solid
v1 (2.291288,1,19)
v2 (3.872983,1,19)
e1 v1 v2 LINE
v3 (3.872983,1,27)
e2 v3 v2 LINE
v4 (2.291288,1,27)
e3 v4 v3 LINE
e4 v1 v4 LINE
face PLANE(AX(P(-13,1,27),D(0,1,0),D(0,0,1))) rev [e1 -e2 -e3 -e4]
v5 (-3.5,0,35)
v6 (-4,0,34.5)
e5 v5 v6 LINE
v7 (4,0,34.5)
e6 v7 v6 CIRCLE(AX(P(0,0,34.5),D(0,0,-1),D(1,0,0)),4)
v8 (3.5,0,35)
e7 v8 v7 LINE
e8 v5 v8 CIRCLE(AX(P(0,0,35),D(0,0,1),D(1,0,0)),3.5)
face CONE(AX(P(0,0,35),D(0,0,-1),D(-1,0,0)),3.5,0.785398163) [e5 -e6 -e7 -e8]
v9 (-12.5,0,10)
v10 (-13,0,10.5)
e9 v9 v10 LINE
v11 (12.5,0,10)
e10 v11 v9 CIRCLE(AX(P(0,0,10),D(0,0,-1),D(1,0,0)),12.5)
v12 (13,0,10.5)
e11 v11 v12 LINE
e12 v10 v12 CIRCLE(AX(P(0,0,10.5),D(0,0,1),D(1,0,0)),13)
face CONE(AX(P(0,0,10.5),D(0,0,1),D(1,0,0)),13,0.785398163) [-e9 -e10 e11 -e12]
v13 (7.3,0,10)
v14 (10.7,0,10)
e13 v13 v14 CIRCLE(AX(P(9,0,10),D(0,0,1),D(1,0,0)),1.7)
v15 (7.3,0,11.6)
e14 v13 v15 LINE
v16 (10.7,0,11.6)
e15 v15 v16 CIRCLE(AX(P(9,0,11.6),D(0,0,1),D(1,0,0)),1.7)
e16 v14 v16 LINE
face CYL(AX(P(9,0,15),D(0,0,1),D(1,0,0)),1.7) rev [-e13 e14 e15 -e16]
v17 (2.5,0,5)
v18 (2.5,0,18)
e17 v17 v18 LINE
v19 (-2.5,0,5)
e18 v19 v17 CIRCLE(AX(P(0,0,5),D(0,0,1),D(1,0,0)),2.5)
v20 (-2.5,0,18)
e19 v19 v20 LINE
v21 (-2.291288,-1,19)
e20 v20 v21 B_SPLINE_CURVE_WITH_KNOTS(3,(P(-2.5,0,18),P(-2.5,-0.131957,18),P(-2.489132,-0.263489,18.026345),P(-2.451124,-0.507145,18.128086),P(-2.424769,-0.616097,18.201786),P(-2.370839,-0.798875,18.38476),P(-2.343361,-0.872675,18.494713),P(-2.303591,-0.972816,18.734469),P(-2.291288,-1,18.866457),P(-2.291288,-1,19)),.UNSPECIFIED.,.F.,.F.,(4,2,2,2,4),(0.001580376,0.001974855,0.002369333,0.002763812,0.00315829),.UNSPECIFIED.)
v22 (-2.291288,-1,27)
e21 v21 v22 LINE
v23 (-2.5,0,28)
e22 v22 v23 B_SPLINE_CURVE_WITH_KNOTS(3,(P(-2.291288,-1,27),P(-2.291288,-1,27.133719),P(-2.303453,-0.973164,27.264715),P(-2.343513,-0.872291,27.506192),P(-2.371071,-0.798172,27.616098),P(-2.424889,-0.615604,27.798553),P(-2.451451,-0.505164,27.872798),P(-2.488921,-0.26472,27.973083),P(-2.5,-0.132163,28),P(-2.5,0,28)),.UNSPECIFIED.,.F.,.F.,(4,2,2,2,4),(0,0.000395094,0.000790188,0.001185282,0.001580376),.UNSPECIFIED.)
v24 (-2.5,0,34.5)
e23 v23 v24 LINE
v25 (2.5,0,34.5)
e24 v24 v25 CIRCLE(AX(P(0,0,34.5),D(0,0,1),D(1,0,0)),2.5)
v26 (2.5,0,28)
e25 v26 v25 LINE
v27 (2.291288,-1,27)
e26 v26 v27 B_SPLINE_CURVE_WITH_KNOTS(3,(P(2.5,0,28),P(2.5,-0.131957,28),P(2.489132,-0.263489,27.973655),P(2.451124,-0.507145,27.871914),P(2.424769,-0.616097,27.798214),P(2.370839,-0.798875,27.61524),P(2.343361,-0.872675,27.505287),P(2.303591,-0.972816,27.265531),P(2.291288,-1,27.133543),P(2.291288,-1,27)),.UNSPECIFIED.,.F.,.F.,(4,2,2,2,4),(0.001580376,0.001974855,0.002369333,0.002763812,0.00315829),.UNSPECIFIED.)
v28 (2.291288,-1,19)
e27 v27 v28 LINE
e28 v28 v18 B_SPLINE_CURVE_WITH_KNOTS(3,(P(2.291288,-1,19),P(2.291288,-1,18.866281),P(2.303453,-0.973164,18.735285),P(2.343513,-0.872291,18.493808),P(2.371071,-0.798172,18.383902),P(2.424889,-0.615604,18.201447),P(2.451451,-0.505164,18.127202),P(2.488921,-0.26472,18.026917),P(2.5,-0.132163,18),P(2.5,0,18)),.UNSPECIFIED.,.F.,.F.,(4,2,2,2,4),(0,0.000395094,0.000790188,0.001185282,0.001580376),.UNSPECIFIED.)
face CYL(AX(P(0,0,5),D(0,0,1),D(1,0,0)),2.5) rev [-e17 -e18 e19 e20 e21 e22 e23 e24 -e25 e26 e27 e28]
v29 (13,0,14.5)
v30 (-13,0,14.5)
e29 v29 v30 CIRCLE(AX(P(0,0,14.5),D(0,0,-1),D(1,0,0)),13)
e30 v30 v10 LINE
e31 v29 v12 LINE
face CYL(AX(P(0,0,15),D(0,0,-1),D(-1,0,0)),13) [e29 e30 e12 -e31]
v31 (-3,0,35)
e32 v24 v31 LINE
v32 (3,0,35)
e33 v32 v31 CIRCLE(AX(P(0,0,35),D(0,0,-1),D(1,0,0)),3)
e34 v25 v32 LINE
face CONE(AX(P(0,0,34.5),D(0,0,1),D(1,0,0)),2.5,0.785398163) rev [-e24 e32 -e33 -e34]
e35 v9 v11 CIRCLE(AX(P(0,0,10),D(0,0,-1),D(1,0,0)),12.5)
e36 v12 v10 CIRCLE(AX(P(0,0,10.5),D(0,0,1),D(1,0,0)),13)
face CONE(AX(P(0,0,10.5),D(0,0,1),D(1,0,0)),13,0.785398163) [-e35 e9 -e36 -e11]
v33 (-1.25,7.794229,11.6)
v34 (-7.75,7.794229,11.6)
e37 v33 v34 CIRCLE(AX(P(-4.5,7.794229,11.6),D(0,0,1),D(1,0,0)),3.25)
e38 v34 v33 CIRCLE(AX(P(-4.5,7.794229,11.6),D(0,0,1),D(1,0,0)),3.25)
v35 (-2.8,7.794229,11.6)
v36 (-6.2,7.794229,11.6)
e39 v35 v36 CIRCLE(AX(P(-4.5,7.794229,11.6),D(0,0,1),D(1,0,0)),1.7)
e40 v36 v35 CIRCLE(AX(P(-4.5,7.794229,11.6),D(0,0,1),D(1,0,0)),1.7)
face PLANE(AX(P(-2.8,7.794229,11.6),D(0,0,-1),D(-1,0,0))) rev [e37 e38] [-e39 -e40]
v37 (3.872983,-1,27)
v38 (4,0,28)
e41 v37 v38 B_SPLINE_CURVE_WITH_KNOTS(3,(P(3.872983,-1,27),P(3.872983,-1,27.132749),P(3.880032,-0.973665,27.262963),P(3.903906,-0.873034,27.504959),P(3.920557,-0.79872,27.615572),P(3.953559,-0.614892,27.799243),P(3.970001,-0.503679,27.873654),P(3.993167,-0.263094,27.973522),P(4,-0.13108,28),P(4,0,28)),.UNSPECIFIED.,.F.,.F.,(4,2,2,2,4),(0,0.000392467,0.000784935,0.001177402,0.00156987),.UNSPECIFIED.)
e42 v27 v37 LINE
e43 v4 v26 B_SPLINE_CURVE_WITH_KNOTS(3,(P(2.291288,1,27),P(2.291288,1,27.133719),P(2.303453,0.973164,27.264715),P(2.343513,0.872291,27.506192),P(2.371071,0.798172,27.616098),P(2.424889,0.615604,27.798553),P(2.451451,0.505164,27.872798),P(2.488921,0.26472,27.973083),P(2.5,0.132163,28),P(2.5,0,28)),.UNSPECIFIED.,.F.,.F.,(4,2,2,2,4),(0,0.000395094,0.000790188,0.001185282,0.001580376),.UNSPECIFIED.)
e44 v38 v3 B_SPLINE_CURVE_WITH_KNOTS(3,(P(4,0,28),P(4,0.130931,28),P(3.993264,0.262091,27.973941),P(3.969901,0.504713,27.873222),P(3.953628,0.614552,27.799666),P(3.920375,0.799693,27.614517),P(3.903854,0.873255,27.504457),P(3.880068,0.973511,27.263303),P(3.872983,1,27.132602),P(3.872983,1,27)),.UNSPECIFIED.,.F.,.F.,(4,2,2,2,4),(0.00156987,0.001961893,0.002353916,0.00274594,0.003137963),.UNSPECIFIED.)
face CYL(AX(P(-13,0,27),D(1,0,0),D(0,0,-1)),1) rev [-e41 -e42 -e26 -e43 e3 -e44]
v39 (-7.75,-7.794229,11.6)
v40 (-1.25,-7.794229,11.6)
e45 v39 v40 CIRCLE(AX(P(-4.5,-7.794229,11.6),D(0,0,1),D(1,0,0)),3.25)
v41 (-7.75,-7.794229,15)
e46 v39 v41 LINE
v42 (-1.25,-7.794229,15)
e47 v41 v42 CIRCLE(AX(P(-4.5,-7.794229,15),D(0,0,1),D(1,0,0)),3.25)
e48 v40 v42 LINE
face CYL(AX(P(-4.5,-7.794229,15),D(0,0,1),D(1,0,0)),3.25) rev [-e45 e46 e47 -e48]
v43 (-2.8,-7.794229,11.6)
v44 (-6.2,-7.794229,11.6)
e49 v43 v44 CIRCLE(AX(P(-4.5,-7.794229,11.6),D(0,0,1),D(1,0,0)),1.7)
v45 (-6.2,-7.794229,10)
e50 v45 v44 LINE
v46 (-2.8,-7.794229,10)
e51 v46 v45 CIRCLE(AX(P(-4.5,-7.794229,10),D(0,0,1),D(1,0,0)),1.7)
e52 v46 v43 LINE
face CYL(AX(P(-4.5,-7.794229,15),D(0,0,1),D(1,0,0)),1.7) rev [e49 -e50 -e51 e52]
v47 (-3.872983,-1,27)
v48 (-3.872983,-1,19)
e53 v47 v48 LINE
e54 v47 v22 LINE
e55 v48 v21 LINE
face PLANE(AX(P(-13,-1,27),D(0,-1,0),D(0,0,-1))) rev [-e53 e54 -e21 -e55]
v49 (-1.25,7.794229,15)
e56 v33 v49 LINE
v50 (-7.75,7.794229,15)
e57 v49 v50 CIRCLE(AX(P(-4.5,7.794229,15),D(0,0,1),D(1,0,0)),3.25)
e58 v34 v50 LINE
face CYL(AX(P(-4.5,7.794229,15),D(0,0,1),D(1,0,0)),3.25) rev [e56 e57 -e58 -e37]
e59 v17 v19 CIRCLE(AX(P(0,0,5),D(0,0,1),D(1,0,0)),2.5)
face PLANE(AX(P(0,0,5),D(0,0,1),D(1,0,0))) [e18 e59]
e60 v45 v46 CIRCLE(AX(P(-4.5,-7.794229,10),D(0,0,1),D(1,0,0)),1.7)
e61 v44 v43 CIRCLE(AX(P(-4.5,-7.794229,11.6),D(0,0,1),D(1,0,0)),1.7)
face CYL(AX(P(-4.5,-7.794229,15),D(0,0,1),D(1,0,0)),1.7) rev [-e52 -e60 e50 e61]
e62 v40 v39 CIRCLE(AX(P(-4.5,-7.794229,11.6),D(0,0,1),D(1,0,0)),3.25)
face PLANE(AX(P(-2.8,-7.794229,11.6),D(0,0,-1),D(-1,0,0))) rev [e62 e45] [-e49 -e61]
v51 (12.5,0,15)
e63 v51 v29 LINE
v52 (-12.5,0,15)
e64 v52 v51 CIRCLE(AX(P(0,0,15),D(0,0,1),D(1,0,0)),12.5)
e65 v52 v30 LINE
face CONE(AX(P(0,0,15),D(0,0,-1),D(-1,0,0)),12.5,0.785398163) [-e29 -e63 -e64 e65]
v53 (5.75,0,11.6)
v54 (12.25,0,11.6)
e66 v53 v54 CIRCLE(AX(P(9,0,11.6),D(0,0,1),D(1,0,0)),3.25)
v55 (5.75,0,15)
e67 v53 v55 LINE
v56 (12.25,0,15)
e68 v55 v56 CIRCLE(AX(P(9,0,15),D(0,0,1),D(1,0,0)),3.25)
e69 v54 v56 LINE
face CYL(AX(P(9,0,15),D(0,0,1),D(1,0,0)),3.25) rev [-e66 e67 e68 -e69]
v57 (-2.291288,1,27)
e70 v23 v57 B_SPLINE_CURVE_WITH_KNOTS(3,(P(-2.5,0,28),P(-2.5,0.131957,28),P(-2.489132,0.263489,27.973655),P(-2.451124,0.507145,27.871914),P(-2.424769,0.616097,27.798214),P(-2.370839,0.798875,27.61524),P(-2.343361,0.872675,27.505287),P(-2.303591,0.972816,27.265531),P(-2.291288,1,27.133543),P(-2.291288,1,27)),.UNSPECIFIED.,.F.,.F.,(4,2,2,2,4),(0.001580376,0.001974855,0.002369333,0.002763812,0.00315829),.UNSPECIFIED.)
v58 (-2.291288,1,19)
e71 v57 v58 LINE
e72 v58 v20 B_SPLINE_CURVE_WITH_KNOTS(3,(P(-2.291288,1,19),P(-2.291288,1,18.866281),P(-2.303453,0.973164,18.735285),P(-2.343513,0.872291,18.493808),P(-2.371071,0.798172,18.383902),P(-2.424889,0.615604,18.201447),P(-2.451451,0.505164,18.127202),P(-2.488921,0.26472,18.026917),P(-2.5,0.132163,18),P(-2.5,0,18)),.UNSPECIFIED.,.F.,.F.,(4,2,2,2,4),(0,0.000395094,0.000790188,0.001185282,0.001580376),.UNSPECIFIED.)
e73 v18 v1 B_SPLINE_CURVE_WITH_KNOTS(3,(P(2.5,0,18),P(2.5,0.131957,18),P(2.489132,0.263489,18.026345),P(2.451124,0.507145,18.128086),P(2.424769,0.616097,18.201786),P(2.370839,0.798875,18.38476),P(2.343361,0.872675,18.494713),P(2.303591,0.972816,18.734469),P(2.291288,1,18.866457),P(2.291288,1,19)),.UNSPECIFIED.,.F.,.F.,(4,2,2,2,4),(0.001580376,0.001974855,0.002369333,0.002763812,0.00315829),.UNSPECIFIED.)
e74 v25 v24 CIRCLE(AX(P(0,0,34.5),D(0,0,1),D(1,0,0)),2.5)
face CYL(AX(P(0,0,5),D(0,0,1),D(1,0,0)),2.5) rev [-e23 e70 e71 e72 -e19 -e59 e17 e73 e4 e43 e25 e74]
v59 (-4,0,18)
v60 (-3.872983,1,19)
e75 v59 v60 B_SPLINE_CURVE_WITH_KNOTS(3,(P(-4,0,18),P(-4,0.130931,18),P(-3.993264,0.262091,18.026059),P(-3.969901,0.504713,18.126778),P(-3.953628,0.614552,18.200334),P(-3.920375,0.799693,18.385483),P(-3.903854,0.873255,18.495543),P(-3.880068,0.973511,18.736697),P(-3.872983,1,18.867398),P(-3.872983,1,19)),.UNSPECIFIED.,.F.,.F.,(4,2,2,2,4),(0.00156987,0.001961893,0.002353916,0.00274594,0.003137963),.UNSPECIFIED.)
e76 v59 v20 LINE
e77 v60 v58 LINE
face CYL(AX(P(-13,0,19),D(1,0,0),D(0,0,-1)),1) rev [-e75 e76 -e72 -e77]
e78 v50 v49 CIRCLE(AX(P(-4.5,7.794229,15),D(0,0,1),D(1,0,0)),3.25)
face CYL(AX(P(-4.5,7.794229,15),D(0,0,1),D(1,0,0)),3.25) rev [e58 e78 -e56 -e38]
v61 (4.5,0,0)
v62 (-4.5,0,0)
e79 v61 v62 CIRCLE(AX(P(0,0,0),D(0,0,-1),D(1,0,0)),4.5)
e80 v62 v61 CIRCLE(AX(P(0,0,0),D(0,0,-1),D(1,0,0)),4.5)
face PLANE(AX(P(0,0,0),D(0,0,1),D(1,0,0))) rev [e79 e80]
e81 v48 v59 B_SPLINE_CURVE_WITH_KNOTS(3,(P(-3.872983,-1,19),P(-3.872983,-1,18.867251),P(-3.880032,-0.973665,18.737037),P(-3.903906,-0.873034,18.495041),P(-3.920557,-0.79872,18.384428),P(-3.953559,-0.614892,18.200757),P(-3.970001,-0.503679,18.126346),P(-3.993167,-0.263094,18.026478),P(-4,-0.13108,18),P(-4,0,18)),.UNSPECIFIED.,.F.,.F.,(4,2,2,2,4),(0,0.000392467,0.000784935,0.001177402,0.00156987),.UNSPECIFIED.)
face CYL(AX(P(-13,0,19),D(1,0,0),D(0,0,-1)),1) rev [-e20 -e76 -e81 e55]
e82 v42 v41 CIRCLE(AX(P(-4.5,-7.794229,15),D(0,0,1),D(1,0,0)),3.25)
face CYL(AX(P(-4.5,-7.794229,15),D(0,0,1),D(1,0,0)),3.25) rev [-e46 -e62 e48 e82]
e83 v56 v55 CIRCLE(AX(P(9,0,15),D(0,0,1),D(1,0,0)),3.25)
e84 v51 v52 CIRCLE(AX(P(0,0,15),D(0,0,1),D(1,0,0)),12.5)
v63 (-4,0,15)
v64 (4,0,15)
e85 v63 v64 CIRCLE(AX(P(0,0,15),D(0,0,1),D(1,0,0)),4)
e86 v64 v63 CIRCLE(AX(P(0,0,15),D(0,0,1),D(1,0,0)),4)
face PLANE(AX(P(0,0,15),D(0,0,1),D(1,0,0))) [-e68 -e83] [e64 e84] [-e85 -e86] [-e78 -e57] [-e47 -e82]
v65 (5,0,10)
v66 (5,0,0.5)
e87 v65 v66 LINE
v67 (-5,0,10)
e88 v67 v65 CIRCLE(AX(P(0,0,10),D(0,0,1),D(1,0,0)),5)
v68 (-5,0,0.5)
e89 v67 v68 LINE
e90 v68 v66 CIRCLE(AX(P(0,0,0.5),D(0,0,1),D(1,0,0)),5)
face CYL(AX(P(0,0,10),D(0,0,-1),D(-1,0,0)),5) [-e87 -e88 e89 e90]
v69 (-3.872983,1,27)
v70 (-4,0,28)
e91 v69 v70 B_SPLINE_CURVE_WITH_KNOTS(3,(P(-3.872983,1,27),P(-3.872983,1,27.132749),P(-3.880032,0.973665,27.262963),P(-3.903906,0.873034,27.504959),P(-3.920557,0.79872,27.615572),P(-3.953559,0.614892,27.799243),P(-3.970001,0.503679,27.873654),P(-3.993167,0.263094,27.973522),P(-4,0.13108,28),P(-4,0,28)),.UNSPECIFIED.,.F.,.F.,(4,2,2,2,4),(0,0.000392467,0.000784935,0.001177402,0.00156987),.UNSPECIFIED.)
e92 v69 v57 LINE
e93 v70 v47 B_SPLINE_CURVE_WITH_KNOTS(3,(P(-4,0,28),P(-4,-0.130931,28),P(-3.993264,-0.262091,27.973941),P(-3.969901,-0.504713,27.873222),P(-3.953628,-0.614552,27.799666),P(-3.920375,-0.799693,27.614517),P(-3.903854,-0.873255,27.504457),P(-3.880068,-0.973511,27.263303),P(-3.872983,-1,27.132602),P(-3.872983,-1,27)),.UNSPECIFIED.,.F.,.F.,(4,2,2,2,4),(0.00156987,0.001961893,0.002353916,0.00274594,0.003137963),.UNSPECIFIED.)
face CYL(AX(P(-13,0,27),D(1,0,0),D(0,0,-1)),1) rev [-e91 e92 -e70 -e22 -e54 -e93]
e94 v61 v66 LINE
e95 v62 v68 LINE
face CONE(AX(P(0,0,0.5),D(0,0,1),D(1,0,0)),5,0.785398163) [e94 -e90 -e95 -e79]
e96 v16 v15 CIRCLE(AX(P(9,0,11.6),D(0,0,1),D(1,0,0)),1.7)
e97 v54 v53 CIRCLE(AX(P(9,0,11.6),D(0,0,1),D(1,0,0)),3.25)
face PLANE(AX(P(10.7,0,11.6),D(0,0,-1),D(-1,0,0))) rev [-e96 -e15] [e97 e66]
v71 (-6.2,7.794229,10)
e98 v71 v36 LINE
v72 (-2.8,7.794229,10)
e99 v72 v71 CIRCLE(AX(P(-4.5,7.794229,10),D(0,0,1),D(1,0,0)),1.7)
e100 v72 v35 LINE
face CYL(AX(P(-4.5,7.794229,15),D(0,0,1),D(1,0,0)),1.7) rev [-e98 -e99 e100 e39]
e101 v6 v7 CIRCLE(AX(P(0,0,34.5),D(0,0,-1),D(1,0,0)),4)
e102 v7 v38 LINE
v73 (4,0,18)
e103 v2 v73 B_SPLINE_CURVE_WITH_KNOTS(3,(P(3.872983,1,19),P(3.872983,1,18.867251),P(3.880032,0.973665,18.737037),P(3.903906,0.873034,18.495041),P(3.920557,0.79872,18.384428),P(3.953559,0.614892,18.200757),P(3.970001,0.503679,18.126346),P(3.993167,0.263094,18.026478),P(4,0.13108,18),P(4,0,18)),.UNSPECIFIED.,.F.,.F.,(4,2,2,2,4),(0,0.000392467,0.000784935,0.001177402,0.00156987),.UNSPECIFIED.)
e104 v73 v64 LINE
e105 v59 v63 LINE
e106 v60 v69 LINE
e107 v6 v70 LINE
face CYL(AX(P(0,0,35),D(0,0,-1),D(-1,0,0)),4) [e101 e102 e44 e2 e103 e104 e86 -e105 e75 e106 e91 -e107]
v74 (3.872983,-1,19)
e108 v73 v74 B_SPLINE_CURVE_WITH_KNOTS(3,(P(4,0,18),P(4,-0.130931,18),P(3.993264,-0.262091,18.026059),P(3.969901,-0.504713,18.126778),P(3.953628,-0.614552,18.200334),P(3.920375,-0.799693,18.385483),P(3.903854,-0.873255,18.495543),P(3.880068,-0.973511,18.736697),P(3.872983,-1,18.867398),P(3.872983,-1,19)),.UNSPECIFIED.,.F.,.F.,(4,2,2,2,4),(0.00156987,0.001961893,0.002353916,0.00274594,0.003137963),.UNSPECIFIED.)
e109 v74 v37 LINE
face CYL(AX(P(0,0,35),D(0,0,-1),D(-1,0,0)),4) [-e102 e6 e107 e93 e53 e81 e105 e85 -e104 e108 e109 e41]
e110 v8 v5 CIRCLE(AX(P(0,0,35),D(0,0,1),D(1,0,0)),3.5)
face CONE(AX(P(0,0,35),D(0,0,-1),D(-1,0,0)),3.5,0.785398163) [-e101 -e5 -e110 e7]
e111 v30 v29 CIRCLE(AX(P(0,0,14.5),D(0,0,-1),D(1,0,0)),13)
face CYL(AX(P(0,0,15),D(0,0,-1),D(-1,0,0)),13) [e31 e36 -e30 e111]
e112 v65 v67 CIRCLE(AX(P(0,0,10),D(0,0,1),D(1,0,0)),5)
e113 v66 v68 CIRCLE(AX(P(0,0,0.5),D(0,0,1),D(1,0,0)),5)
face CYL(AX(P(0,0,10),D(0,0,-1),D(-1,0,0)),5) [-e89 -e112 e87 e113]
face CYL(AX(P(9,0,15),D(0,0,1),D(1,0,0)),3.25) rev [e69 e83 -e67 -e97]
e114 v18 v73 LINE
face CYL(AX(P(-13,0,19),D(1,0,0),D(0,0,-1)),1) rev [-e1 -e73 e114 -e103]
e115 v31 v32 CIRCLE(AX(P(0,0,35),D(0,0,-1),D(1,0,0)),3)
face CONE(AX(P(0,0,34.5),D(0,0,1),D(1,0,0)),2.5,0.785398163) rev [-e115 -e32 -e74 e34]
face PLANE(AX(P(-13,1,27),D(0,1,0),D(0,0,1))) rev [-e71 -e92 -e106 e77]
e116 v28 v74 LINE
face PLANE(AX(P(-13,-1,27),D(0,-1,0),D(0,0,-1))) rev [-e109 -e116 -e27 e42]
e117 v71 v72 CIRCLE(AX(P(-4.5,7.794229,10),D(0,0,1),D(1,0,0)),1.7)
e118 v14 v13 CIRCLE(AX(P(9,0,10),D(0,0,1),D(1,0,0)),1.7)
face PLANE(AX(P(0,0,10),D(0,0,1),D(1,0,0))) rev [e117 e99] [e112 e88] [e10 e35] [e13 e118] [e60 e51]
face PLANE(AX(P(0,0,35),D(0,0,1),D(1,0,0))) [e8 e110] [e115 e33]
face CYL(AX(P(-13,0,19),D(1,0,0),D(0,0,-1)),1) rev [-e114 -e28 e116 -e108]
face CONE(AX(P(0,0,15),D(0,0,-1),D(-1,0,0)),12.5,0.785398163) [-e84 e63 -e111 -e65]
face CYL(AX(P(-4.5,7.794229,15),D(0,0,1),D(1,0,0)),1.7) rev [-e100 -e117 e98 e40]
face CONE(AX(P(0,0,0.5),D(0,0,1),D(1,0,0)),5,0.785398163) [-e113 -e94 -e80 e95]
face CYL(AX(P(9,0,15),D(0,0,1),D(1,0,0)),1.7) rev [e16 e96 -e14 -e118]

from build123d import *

# Parameters (mm, degrees)
SKETCH1_R                                           = 5
BOSS_EXTRUDE1_DEPTH                                 = 10
SKETCH2_R                                           = 13
BOSS_EXTRUDE2_DEPTH                                 = 5
SKETCH3_R                                           = 4
BOSS_EXTRUDE3_DEPTH                                 = 20
SKETCH4_R                                           = 2.5
CUT_EXTRUDE1_DEPTH                                  = 30
CBORE_FOR_M3_HEX_SOCKET_HEAD_CAP_SCREW1_D           = 3.4
CBORE_FOR_M3_HEX_SOCKET_HEAD_CAP_SCREW1_CBORE_D     = 6.5
CBORE_FOR_M3_HEX_SOCKET_HEAD_CAP_SCREW1_CBORE_DEPTH = 3.4
CIRPATTERN1_COUNT                                   = 3
CUT_EXTRUDE2_DEPTH                                  = 42.024382994
CHAMFER1_SIZE                                       = 0.5


with BuildPart() as part:
    # Sketch1 → Boss-Extrude1 (new body)
    with BuildSketch(Plane.XY):
        Circle(SKETCH1_R)
    extrude(amount=BOSS_EXTRUDE1_DEPTH)

    # Sketch2 → Boss-Extrude2 (add)
    with BuildSketch(Plane.XY.offset(10)):
        Circle(SKETCH2_R)
    extrude(amount=BOSS_EXTRUDE2_DEPTH)

    # Sketch3 → Boss-Extrude3 (add)
    with BuildSketch(Plane.XY.offset(15)):
        Circle(SKETCH3_R)
    extrude(amount=BOSS_EXTRUDE3_DEPTH)

    # Sketch4 → Cut-Extrude1 (cut)
    with BuildSketch(Plane.XY.offset(35)):
        Circle(SKETCH4_R)
    extrude(amount=-CUT_EXTRUDE1_DEPTH, mode=Mode.SUBTRACT)

    # CBORE for M3 Hex Socket Head Cap Screw1 (through all)
    with Locations(Plane.XY.offset(15)):
        with Locations((9, 0)):
            cbore_for_m3_hex_socket_head_cap_screw1 = CounterBoreHole(CBORE_FOR_M3_HEX_SOCKET_HEAD_CAP_SCREW1_D / 2, CBORE_FOR_M3_HEX_SOCKET_HEAD_CAP_SCREW1_CBORE_D / 2, CBORE_FOR_M3_HEX_SOCKET_HEAD_CAP_SCREW1_CBORE_DEPTH)

    # CirPattern1: CBORE for M3 Hex Socket Head Cap Screw1 ×3 about axis
    cirpattern1_axis = Axis((0, 0, 0), (0, 0, 1))
    for i in range(1, CIRPATTERN1_COUNT):
        add(cbore_for_m3_hex_socket_head_cap_screw1.rotate(cirpattern1_axis, i * 360 / CIRPATTERN1_COUNT), mode=Mode.SUBTRACT)

    # Sketch7 → Cut-Extrude2 (cut, through all)
    with BuildSketch(Plane(origin=(4, 0, 0), x_dir=(0, 0, -1), z_dir=(1, 0, 0))):
        with BuildLine():
            Line((-27, 1), (-19, 1))
            ThreePointArc((-19, 1), (-18, 0), (-19, -1))
            Line((-19, -1), (-27, -1))
            ThreePointArc((-27, -1), (-28, 0), (-27, 1))
        make_face()
    extrude(amount=-CUT_EXTRUDE2_DEPTH, mode=Mode.SUBTRACT)

    # Chamfer1
    chamfer1_edges = [part.edges().sort_by_distance(p)[0] for p in [
        (-4, 0, 35),
        (-2.5, 0, 35),
        (-5, 0, 0),
        (-13, 0, 10),
        (-13, 0, 15),
    ]]
    chamfer(chamfer1_edges, length=CHAMFER1_SIZE)


solid = part.part
